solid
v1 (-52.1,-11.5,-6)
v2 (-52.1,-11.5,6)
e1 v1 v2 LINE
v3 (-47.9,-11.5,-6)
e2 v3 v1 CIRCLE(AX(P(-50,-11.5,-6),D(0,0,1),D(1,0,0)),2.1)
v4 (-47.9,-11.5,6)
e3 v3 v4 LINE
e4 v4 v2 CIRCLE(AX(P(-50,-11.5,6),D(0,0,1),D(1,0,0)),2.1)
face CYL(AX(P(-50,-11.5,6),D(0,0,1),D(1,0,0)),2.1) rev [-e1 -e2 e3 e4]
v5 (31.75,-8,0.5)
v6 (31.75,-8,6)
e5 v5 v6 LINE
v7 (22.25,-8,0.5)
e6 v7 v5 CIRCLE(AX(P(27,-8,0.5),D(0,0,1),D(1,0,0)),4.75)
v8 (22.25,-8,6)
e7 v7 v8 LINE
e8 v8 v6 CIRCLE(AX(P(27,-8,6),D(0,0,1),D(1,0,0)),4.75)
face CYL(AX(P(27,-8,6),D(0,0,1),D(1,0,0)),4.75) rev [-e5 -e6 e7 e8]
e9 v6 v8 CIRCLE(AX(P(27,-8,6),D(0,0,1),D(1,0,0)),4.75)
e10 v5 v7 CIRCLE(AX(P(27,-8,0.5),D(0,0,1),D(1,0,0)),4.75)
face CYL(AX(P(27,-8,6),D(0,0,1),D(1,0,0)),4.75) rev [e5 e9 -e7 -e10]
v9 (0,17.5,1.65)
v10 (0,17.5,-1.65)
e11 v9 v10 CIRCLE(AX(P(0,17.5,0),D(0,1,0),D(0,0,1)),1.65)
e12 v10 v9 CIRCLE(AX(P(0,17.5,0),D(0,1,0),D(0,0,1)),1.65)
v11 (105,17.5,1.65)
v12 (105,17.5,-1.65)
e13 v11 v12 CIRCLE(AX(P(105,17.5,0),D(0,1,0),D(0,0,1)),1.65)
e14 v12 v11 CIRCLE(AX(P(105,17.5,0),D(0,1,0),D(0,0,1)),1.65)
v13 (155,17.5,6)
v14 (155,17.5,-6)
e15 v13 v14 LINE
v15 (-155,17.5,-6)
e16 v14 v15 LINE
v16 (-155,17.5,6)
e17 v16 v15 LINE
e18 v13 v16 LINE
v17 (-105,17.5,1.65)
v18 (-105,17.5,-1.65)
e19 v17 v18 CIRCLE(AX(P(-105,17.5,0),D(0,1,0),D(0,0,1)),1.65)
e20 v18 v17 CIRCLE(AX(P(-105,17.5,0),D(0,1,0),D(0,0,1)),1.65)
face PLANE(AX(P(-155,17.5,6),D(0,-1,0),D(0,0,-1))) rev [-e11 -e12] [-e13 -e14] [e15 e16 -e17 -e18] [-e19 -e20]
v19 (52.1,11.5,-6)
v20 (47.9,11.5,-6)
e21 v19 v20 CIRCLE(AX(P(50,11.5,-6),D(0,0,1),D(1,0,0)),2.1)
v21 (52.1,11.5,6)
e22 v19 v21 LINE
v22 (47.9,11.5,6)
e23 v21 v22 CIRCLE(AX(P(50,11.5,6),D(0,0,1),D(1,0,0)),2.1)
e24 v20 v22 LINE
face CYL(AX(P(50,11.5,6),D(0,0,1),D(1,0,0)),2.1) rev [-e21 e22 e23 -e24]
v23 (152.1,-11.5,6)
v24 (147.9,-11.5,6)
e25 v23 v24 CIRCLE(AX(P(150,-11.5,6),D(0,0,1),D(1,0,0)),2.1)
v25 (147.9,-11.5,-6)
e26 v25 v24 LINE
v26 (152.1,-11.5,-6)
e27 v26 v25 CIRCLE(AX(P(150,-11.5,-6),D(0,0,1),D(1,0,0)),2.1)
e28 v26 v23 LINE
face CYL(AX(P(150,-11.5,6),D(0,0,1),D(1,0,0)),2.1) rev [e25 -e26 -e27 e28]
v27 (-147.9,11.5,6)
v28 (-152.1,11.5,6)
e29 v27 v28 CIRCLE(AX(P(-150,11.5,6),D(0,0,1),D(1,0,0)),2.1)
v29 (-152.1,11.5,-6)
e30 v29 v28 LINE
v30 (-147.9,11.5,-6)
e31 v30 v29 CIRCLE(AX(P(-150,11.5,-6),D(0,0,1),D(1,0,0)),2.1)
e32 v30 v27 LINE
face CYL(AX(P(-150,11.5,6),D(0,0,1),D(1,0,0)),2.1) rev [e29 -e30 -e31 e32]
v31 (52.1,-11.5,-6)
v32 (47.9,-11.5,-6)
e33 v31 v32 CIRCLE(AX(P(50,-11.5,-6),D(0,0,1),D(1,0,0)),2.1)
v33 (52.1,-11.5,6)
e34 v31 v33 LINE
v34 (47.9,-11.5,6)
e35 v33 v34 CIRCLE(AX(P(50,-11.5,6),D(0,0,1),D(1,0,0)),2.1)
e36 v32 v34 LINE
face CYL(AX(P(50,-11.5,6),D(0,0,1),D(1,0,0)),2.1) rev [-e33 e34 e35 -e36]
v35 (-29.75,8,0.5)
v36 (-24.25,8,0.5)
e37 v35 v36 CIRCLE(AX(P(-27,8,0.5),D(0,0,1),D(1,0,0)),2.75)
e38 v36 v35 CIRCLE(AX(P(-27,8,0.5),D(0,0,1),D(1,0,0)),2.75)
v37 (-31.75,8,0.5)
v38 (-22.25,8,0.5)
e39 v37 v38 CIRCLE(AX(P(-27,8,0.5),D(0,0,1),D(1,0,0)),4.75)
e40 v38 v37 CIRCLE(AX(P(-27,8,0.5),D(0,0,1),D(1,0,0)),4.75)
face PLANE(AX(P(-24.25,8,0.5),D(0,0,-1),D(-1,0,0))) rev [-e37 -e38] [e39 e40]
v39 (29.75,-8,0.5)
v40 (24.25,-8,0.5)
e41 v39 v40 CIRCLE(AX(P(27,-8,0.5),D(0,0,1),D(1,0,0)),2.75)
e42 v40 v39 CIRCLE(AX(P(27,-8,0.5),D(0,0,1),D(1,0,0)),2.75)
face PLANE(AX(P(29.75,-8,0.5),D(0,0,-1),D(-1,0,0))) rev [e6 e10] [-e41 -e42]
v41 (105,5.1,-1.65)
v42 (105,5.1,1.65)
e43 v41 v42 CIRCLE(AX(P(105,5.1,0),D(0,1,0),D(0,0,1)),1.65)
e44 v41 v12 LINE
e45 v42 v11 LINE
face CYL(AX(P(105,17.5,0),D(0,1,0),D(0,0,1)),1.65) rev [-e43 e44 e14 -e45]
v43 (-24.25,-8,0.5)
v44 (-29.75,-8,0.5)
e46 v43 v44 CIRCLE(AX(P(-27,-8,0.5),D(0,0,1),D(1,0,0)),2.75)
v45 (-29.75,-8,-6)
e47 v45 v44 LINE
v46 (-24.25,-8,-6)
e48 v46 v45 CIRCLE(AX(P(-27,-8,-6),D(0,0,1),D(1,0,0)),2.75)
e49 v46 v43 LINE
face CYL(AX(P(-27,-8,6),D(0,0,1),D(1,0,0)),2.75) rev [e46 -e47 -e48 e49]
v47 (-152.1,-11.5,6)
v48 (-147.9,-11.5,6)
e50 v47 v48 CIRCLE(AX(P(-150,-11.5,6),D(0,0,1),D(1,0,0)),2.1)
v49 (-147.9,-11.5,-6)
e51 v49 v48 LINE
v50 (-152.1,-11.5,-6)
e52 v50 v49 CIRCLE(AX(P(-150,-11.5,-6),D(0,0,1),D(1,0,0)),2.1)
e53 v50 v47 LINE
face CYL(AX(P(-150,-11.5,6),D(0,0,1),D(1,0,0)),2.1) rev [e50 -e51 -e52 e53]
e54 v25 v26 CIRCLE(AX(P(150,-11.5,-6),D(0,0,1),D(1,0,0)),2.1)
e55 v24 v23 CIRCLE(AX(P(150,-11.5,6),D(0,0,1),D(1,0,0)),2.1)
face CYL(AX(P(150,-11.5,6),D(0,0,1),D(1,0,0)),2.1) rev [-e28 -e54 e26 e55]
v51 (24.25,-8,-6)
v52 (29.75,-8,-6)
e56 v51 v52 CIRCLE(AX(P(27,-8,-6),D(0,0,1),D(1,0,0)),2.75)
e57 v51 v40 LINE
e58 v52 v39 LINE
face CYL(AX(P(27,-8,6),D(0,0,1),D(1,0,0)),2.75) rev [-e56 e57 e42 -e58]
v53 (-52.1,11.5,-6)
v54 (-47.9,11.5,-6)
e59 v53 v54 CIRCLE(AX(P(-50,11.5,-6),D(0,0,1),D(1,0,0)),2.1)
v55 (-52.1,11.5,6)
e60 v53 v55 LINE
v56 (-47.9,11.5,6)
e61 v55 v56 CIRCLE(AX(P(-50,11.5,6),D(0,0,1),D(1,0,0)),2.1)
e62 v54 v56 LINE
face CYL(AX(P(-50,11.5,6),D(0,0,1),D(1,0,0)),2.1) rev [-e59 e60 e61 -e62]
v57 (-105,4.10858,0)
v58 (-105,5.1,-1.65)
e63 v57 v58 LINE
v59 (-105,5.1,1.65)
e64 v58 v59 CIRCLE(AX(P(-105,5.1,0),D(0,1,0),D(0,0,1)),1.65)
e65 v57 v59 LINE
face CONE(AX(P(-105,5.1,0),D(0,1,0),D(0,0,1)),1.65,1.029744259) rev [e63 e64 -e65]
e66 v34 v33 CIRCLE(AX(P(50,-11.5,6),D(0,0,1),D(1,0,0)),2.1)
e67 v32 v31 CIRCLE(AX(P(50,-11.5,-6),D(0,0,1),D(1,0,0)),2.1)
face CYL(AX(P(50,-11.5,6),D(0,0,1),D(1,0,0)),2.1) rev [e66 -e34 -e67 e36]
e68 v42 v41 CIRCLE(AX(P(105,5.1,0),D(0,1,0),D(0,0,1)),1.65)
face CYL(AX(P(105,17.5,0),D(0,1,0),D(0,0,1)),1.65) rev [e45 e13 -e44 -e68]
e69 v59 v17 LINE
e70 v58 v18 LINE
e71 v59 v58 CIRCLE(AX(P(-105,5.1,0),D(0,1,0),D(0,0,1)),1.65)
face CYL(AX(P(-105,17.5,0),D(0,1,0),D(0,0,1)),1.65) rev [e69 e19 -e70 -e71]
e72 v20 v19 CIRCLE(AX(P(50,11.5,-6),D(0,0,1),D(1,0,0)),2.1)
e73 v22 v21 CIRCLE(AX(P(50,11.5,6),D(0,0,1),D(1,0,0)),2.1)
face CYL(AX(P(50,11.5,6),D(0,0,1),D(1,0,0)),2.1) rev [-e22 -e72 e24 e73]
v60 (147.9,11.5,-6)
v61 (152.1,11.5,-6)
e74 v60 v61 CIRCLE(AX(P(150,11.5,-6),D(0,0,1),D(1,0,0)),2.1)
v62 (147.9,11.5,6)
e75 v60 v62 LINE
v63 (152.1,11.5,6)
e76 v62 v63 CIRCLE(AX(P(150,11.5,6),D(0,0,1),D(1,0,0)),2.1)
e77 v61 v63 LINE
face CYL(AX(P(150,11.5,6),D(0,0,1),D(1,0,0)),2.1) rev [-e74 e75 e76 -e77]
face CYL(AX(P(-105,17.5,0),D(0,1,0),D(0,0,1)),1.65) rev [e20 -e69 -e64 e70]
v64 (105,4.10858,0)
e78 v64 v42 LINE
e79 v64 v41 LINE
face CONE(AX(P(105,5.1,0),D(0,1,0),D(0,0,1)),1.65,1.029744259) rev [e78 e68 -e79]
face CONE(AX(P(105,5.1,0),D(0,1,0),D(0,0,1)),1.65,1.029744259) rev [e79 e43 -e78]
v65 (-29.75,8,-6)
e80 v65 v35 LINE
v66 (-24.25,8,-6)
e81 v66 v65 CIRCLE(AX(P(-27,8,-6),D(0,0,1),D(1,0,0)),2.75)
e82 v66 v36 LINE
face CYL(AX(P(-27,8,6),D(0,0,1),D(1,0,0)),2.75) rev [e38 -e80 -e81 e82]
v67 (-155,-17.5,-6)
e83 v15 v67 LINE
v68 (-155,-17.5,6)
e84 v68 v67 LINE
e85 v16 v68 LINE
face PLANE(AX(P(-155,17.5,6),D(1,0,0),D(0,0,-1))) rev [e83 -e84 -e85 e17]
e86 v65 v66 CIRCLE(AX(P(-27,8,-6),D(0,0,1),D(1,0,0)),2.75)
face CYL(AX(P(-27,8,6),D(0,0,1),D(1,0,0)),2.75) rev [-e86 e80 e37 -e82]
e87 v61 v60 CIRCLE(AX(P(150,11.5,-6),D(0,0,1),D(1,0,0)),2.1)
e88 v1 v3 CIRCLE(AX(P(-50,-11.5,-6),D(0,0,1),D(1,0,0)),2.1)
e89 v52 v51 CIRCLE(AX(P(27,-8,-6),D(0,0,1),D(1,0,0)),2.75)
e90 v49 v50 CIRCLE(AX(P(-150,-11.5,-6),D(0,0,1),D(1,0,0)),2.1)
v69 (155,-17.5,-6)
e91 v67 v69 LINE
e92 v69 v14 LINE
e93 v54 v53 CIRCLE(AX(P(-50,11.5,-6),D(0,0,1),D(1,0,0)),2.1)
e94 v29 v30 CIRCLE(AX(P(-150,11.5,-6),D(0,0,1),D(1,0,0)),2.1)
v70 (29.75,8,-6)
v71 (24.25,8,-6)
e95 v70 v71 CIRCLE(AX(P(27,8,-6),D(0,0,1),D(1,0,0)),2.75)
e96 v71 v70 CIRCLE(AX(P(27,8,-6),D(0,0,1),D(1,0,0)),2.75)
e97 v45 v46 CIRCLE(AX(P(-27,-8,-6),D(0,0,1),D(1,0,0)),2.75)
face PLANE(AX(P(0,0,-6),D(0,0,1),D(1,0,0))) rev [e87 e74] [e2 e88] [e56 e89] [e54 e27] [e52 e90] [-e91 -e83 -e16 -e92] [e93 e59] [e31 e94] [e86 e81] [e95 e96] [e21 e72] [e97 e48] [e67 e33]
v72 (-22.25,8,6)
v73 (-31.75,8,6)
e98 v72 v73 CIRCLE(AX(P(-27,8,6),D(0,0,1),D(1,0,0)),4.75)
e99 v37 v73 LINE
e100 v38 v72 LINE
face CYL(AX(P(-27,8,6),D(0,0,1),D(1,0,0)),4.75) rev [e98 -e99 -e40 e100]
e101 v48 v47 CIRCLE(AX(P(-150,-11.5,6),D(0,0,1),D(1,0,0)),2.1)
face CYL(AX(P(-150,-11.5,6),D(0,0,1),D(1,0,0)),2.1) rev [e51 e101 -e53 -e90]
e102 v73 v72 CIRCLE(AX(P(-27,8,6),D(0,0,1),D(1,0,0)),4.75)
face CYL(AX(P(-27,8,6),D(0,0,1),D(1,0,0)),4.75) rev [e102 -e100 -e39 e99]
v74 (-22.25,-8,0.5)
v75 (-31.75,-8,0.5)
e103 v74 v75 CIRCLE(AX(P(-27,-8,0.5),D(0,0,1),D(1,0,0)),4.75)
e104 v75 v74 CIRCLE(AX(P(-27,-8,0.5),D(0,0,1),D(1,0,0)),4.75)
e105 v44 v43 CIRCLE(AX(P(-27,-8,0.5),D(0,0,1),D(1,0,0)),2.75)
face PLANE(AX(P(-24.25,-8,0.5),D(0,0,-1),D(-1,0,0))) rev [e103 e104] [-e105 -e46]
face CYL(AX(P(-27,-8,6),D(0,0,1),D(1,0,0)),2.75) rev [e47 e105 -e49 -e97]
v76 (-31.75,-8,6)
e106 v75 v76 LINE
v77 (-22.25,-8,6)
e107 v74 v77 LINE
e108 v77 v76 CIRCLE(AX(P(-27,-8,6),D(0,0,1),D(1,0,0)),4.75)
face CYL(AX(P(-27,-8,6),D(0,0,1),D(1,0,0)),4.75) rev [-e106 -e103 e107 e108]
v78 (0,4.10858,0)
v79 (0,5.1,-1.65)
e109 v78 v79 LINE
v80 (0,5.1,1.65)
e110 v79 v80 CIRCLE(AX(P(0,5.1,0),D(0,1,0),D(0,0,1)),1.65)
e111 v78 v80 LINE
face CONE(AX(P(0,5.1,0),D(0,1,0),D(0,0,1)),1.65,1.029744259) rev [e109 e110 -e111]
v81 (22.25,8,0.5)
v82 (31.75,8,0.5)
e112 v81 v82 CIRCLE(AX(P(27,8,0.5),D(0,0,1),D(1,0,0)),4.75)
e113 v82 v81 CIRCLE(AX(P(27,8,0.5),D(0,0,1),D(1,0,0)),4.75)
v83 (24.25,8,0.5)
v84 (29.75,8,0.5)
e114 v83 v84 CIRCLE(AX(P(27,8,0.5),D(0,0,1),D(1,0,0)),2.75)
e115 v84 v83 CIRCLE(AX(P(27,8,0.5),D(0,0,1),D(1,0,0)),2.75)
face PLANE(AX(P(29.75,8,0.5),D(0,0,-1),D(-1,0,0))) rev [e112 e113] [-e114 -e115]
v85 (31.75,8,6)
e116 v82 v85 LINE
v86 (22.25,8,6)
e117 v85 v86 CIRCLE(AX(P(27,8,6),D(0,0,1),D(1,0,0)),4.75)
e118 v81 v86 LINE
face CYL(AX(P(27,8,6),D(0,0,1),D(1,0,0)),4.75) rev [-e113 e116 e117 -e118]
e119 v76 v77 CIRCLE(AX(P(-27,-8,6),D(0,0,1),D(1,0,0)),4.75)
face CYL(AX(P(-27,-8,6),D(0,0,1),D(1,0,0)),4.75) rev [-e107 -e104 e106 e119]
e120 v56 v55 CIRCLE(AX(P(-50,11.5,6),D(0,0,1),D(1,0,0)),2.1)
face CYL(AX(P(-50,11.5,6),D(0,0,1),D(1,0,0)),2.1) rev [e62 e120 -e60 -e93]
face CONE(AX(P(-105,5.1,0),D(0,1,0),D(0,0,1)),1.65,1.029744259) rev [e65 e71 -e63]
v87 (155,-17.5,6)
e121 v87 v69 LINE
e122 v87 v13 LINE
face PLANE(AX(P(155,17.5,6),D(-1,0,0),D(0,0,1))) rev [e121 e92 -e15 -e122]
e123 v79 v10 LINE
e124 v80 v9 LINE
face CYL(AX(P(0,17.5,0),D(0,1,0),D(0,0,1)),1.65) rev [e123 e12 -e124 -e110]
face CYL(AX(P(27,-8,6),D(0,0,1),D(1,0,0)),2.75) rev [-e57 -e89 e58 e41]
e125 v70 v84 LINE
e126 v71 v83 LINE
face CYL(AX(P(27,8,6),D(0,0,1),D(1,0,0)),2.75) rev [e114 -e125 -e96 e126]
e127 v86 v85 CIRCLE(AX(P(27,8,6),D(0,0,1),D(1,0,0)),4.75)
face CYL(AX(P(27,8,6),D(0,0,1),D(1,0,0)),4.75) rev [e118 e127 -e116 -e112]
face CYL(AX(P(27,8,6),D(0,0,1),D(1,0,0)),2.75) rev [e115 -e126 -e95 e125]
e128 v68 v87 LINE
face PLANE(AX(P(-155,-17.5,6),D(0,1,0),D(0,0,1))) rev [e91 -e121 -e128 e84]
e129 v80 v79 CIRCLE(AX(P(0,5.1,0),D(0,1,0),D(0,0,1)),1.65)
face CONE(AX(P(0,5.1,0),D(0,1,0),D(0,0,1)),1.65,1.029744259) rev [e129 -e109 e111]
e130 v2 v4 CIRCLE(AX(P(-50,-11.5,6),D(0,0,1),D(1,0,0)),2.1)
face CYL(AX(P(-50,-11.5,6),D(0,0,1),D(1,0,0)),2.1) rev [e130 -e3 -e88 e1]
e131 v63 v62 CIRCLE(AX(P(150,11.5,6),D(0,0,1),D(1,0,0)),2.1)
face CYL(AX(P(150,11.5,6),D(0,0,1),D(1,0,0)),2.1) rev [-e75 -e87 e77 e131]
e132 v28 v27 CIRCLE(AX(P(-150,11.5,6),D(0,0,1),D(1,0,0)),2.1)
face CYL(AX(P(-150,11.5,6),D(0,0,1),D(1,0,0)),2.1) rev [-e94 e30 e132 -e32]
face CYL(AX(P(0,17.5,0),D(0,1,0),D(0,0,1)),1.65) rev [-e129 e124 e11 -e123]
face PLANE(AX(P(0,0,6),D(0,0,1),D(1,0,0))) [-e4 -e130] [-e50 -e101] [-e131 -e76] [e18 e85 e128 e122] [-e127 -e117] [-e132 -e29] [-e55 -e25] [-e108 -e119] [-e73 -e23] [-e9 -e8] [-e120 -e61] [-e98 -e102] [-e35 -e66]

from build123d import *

# Parameters (mm, degrees)
SKETCH_1_W                     = 310
SKETCH_1_H                     = 35
EXTRUDE_1_DEPTH                = 6
HOLE_WIZARD_M5_1_D             = 4.2
PATTERN_LINEAR_2_COUNT         = 4
PATTERN_LINEAR_2_PITCH         = 100
HOLE_WIZARD_M5_1_2_D           = 5.5
HOLE_WIZARD_M5_1_2_CBORE_D     = 9.5
HOLE_WIZARD_M5_1_2_CBORE_DEPTH = 5.5
HOLE_WIZARD_M4_1_D             = 3.3
HOLE_WIZARD_M4_1_DEPTH         = 12.4
HOLE_WIZARD_M4_1_TIP           = 0.991420021


with BuildPart() as part:
    # 草图1 → 凸台-拉伸1 (new, symmetric)
    with BuildSketch(Plane.XY):
        Rectangle(SKETCH_1_W, SKETCH_1_H)
    extrude(amount=EXTRUDE_1_DEPTH, both=True)

    # Hole Wizard M5 _1 (through all)
    with Locations(Plane.XY.offset(6)):
        with Locations((150, 11.5), (150, -11.5)):
            hole_wizard_m5_1 = Hole(HOLE_WIZARD_M5_1_D / 2)

    # 阵列(线性)2: Hole Wizard M5 _1 ×4
    with Locations(*[(-i * PATTERN_LINEAR_2_PITCH, 0, 0) for i in range(1, PATTERN_LINEAR_2_COUNT)]):
        add(hole_wizard_m5_1, mode=Mode.SUBTRACT)

    # Hole Wizard M5 _1 2 (through all)
    with Locations(Plane.XY.offset(6)):
        with Locations((-27, 8), (-27, -8), (27, 8), (27, -8)):
            CounterBoreHole(HOLE_WIZARD_M5_1_2_D / 2, HOLE_WIZARD_M5_1_2_CBORE_D / 2, HOLE_WIZARD_M5_1_2_CBORE_DEPTH)

    # M4 螺纹孔1
    with Locations(Plane(origin=(0, 17.5, 0), x_dir=(1, 0, 0), z_dir=(0, 1, 0))):
        with Locations((105, 0), (0, 0), (-105, 0)):
            Hole(HOLE_WIZARD_M4_1_D / 2, depth=HOLE_WIZARD_M4_1_DEPTH)
            with Locations((0, 0, -(HOLE_WIZARD_M4_1_DEPTH + HOLE_WIZARD_M4_1_TIP / 2))):  # 118° drill point
                Cone(0, HOLE_WIZARD_M4_1_D / 2, HOLE_WIZARD_M4_1_TIP, mode=Mode.SUBTRACT)


solid = part.part
